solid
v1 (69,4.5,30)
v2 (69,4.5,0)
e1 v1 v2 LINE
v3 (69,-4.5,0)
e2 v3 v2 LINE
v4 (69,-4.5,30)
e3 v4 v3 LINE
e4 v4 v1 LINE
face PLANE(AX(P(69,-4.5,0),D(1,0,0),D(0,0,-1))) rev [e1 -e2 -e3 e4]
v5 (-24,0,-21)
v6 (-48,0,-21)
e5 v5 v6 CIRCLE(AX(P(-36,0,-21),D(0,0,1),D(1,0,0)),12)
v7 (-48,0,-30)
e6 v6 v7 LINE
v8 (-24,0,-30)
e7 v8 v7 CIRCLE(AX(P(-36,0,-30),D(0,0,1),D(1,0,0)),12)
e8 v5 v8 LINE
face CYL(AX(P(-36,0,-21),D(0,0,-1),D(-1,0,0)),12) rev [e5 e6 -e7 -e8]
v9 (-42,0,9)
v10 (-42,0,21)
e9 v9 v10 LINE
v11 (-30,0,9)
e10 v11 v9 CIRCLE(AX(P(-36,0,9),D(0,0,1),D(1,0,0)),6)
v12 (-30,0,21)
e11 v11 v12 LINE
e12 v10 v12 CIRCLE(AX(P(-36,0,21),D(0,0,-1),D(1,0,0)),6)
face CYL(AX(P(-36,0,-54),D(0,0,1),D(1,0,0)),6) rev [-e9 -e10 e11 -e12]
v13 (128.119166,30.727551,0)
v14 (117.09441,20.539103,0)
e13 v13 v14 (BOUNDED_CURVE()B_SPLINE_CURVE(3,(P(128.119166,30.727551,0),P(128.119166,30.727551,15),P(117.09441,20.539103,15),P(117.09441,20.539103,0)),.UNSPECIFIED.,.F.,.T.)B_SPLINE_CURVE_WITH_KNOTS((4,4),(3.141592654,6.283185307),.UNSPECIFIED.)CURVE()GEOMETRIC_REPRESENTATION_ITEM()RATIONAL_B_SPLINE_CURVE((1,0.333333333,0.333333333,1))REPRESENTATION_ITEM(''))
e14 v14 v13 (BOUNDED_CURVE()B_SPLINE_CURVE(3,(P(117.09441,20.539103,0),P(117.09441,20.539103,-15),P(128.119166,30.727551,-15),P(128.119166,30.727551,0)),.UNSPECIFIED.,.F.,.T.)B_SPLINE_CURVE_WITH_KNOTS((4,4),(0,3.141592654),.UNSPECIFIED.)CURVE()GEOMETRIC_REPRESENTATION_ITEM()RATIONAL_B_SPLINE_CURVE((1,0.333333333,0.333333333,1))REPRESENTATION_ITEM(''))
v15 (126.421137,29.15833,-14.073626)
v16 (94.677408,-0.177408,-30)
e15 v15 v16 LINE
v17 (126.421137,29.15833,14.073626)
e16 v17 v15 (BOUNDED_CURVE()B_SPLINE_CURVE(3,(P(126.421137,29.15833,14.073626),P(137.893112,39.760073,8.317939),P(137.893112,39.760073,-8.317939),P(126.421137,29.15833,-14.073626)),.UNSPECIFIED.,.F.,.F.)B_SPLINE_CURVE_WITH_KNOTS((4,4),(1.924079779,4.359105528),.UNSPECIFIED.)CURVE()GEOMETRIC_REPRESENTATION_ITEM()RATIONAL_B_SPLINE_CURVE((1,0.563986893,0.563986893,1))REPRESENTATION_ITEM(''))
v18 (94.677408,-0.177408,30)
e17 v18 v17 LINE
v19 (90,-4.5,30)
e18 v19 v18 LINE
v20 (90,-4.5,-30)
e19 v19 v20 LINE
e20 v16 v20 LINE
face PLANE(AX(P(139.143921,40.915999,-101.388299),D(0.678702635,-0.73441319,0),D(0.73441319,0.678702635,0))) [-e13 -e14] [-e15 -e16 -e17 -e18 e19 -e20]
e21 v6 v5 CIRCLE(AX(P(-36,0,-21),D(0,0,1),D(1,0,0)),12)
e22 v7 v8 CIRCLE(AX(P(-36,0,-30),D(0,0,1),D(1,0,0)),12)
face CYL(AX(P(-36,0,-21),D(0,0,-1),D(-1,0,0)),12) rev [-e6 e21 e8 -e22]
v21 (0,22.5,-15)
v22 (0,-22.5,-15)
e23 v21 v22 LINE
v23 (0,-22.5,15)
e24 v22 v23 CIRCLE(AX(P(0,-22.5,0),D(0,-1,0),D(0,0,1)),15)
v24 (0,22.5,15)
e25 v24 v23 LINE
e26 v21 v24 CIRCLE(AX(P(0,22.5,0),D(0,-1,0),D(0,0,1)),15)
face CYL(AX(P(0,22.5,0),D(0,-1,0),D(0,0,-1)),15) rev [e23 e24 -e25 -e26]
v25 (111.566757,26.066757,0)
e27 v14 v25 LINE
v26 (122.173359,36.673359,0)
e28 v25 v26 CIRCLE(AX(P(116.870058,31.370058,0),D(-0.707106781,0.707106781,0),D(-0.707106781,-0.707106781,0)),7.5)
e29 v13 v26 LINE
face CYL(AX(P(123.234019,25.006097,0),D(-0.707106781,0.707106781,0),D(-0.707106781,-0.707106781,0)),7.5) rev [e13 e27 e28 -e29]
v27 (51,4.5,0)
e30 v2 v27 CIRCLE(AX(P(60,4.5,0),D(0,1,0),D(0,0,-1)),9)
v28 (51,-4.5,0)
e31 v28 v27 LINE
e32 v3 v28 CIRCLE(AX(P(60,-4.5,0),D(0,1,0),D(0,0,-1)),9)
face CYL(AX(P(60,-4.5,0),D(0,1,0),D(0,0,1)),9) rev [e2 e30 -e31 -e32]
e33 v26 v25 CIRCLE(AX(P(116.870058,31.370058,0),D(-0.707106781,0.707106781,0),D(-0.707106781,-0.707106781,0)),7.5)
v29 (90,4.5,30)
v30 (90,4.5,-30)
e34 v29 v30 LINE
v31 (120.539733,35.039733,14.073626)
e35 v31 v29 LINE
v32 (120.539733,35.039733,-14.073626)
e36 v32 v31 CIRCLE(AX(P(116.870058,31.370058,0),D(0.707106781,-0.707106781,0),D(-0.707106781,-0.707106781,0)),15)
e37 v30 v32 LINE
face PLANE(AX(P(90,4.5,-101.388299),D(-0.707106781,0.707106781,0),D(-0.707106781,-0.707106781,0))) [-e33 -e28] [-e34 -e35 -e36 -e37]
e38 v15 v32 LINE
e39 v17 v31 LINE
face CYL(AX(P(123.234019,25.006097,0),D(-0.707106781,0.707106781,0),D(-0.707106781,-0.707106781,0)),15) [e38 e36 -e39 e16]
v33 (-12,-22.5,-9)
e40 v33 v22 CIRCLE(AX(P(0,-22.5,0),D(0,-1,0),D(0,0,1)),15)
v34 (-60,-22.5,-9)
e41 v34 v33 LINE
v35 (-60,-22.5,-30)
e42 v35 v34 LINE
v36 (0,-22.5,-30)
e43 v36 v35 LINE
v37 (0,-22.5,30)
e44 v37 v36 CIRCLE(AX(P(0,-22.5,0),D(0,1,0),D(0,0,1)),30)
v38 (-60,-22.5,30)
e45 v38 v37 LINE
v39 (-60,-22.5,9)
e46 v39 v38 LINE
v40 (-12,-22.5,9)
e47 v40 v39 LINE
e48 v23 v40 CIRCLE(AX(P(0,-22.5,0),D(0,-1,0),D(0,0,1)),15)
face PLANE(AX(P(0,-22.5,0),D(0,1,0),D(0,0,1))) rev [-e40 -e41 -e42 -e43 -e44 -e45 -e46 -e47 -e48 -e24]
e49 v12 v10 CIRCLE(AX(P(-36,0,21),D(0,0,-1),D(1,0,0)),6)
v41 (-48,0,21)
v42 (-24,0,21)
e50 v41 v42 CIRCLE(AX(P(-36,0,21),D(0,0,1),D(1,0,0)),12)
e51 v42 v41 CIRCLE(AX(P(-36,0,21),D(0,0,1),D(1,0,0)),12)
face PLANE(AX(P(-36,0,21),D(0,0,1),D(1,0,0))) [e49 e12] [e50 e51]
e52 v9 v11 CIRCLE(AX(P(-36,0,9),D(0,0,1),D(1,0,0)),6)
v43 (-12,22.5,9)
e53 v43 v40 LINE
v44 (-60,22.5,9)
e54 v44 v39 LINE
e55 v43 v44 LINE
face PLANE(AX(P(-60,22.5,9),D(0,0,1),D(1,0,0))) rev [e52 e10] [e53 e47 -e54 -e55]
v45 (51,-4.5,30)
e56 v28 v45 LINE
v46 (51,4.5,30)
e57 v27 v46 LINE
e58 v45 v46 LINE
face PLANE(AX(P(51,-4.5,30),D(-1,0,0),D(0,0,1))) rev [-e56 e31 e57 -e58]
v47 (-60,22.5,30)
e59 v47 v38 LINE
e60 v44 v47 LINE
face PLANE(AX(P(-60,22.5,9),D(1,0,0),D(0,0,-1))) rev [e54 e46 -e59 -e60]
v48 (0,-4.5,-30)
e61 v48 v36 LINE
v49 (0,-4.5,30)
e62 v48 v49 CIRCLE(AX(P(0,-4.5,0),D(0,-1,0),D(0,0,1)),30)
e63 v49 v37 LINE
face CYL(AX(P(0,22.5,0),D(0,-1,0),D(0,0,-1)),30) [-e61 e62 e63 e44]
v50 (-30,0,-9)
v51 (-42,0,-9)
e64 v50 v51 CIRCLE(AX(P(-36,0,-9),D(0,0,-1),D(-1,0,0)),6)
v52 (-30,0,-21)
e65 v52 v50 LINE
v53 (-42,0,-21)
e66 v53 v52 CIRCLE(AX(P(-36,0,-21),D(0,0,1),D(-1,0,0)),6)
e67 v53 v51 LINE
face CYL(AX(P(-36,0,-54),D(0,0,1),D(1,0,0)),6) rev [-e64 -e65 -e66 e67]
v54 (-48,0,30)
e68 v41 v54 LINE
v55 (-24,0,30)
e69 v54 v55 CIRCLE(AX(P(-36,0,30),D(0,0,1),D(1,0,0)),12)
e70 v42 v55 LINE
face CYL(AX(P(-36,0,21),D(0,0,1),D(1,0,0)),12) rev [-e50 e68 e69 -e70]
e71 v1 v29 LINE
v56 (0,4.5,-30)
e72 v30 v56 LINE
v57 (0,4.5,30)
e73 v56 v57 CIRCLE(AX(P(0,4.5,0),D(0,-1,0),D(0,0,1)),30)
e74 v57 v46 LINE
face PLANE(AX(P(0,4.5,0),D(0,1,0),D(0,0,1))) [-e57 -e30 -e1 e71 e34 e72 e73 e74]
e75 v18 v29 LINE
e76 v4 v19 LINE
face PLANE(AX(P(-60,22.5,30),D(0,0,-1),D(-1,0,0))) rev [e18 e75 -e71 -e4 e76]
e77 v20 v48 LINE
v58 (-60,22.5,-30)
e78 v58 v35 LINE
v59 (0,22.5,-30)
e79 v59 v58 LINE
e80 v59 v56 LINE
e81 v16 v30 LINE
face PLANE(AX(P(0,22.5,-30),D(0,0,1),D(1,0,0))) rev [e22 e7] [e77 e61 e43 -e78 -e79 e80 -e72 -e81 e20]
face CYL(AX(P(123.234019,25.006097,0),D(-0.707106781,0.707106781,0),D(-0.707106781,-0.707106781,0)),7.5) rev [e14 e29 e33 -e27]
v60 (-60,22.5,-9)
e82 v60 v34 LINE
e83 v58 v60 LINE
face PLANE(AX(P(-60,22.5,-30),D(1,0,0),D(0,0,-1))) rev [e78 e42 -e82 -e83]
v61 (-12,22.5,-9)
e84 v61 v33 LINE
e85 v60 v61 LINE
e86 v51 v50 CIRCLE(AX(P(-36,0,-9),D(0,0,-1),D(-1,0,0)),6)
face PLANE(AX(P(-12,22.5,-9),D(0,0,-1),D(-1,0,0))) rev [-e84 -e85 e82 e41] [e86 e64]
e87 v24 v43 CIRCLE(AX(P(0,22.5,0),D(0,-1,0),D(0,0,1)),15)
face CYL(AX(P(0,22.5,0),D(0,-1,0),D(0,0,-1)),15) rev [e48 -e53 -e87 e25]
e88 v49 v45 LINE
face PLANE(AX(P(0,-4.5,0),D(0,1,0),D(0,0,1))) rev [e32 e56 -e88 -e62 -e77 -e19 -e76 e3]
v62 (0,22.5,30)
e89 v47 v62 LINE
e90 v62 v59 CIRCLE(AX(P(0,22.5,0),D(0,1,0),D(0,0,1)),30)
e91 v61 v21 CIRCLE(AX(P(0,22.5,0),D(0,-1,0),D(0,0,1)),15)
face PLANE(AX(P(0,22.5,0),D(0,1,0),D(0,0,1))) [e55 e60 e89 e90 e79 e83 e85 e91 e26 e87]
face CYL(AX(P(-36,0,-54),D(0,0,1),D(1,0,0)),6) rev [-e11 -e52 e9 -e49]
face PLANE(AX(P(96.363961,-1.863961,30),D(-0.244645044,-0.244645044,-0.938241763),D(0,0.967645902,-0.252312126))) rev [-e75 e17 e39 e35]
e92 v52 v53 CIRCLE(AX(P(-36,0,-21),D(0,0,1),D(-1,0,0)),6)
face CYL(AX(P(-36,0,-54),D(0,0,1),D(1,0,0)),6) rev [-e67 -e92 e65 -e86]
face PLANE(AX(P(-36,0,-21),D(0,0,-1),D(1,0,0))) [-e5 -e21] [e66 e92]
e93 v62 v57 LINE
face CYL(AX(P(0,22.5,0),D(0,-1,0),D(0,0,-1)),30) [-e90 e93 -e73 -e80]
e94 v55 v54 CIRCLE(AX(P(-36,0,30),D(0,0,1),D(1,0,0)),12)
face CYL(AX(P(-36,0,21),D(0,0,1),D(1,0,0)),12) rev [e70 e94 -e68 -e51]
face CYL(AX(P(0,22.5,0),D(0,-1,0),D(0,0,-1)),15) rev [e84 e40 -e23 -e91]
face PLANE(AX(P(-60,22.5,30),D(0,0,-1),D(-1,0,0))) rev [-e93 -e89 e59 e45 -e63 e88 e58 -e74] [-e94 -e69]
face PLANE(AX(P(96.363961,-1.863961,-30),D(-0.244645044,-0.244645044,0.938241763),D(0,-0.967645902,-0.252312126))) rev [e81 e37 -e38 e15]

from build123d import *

# Parameters (mm, degrees)
CLEVIS_BODY_DEPTH    = 22.5
CROSS_HOLE_SKETCH_R  = 6
CROSS_HOLE_DEPTH     = 84
COUNTERBORE_SKETCH_R = 12
COUNTERBORE_24_DEPTH = 9
MOUNTING_START       = -22.5
MOUNTING_TAB_DEPTH   = 4.5
ANGLED_LIP_DEPTH     = 60
RELIEF_CUT_DEPTH     = 9
TAB_SLOT_SKETCH_R    = 7.5
TAB_SLOT_DEPTH       = 9


with BuildPart() as part:
    # Clevis Body Sketch → Clevis Body (new, symmetric)
    with BuildSketch(Plane(origin=(0, 0, 0), x_dir=(1, 0, 0), z_dir=(0, 1, 0))):
        with BuildLine():
            Line((-12, 9), (-60, 9))
            Line((-60, 9), (-60, 30))
            Line((-60, 30), (0, 30))
            ThreePointArc((0, 30), (30, 0), (0, -30))
            Line((0, -30), (-60, -30))
            Line((-60, -30), (-60, -9))
            Line((-60, -9), (-12, -9))
            ThreePointArc((-12, -9), (15, 0), (-12, 9))
        make_face()
    extrude(amount=CLEVIS_BODY_DEPTH, both=True)

    # Cross Hole Sketch → Cross Hole (cut)
    with BuildSketch(Plane.XY.offset(30)):
        with Locations((-36, 0)):
            Circle(CROSS_HOLE_SKETCH_R)
    extrude(amount=-CROSS_HOLE_DEPTH, mode=Mode.SUBTRACT)

    # Counterbore Sketch → Counterbore Ø24 (cut)
    with BuildSketch(Plane.XY.offset(30)):
        with Locations((-36, 0)):
            Circle(COUNTERBORE_SKETCH_R)
    counterbore_24 = extrude(amount=-COUNTERBORE_24_DEPTH, mode=Mode.SUBTRACT)

    # Counterbore Mirror: Counterbore Ø24 across plane
    add(counterbore_24.mirror(Plane.XY), mode=Mode.SUBTRACT)

    # Mounting Tab Sketch → Mounting Tab (add, symmetric)
    with BuildSketch(Plane(origin=(0, 22.5, 0), x_dir=(1, 0, 0), z_dir=(0, 1, 0)).offset(MOUNTING_START)):
        with BuildLine():
            Line((0, 30), (90, 30))
            Line((90, 30), (90, -30))
            Line((90, -30), (0, -30))
            ThreePointArc((0, -30), (30, 0), (0, 30))
        make_face()
    extrude(amount=MOUNTING_TAB_DEPTH, both=True)

    # Angled Lip Sketch → Angled Lip (add)
    with BuildSketch(Plane.XY.offset(30)):
        Polygon((90, -4.5), (90, 4.5), (132.779960262, 47.279960262), (139.143921292, 40.915999231), align=None)
    extrude(amount=-ANGLED_LIP_DEPTH)

    # Relief Cut Sketch → Relief Cut (cut)
    with BuildSketch(Plane(origin=(0, 4.5, 0), x_dir=(1, 0, 0), z_dir=(0, 1, 0))):
        with BuildLine():
            Line((51, -30), (51, 0))
            ThreePointArc((51, 0), (60, 9), (69, 0))
            Line((69, 0), (69, -30))
            Line((69, -30), (51, -30))
        make_face()
    extrude(amount=-RELIEF_CUT_DEPTH, mode=Mode.SUBTRACT)

    # Tab Slot Sketch → Tab Slot (cut)
    with BuildSketch(Plane(origin=(42.75, -42.75, 0), x_dir=(0, 0, 1), z_dir=(-0.7071067811865488, 0.7071067811865464, 0))):
        with Locations(Location((0, 104.821590822, 0), (0, 0, 270))):
            Circle(TAB_SLOT_SKETCH_R)
        with BuildLine():
            Line((-30, 66.821590822), (-14.073626439, 110.011295906))
            ThreePointArc((-14.073626439, 110.011295906), (0, 119.821590822), (14.073626439, 110.011295906))
            Line((14.073626439, 110.011295906), (30, 66.821590822))
            Line((30, 66.821590822), (30, 127.321590822))
            Line((30, 127.321590822), (-30, 127.321590822))
            Line((-30, 127.321590822), (-30, 66.821590822))
        make_face()
    extrude(amount=-TAB_SLOT_DEPTH, mode=Mode.SUBTRACT)


solid = part.part
